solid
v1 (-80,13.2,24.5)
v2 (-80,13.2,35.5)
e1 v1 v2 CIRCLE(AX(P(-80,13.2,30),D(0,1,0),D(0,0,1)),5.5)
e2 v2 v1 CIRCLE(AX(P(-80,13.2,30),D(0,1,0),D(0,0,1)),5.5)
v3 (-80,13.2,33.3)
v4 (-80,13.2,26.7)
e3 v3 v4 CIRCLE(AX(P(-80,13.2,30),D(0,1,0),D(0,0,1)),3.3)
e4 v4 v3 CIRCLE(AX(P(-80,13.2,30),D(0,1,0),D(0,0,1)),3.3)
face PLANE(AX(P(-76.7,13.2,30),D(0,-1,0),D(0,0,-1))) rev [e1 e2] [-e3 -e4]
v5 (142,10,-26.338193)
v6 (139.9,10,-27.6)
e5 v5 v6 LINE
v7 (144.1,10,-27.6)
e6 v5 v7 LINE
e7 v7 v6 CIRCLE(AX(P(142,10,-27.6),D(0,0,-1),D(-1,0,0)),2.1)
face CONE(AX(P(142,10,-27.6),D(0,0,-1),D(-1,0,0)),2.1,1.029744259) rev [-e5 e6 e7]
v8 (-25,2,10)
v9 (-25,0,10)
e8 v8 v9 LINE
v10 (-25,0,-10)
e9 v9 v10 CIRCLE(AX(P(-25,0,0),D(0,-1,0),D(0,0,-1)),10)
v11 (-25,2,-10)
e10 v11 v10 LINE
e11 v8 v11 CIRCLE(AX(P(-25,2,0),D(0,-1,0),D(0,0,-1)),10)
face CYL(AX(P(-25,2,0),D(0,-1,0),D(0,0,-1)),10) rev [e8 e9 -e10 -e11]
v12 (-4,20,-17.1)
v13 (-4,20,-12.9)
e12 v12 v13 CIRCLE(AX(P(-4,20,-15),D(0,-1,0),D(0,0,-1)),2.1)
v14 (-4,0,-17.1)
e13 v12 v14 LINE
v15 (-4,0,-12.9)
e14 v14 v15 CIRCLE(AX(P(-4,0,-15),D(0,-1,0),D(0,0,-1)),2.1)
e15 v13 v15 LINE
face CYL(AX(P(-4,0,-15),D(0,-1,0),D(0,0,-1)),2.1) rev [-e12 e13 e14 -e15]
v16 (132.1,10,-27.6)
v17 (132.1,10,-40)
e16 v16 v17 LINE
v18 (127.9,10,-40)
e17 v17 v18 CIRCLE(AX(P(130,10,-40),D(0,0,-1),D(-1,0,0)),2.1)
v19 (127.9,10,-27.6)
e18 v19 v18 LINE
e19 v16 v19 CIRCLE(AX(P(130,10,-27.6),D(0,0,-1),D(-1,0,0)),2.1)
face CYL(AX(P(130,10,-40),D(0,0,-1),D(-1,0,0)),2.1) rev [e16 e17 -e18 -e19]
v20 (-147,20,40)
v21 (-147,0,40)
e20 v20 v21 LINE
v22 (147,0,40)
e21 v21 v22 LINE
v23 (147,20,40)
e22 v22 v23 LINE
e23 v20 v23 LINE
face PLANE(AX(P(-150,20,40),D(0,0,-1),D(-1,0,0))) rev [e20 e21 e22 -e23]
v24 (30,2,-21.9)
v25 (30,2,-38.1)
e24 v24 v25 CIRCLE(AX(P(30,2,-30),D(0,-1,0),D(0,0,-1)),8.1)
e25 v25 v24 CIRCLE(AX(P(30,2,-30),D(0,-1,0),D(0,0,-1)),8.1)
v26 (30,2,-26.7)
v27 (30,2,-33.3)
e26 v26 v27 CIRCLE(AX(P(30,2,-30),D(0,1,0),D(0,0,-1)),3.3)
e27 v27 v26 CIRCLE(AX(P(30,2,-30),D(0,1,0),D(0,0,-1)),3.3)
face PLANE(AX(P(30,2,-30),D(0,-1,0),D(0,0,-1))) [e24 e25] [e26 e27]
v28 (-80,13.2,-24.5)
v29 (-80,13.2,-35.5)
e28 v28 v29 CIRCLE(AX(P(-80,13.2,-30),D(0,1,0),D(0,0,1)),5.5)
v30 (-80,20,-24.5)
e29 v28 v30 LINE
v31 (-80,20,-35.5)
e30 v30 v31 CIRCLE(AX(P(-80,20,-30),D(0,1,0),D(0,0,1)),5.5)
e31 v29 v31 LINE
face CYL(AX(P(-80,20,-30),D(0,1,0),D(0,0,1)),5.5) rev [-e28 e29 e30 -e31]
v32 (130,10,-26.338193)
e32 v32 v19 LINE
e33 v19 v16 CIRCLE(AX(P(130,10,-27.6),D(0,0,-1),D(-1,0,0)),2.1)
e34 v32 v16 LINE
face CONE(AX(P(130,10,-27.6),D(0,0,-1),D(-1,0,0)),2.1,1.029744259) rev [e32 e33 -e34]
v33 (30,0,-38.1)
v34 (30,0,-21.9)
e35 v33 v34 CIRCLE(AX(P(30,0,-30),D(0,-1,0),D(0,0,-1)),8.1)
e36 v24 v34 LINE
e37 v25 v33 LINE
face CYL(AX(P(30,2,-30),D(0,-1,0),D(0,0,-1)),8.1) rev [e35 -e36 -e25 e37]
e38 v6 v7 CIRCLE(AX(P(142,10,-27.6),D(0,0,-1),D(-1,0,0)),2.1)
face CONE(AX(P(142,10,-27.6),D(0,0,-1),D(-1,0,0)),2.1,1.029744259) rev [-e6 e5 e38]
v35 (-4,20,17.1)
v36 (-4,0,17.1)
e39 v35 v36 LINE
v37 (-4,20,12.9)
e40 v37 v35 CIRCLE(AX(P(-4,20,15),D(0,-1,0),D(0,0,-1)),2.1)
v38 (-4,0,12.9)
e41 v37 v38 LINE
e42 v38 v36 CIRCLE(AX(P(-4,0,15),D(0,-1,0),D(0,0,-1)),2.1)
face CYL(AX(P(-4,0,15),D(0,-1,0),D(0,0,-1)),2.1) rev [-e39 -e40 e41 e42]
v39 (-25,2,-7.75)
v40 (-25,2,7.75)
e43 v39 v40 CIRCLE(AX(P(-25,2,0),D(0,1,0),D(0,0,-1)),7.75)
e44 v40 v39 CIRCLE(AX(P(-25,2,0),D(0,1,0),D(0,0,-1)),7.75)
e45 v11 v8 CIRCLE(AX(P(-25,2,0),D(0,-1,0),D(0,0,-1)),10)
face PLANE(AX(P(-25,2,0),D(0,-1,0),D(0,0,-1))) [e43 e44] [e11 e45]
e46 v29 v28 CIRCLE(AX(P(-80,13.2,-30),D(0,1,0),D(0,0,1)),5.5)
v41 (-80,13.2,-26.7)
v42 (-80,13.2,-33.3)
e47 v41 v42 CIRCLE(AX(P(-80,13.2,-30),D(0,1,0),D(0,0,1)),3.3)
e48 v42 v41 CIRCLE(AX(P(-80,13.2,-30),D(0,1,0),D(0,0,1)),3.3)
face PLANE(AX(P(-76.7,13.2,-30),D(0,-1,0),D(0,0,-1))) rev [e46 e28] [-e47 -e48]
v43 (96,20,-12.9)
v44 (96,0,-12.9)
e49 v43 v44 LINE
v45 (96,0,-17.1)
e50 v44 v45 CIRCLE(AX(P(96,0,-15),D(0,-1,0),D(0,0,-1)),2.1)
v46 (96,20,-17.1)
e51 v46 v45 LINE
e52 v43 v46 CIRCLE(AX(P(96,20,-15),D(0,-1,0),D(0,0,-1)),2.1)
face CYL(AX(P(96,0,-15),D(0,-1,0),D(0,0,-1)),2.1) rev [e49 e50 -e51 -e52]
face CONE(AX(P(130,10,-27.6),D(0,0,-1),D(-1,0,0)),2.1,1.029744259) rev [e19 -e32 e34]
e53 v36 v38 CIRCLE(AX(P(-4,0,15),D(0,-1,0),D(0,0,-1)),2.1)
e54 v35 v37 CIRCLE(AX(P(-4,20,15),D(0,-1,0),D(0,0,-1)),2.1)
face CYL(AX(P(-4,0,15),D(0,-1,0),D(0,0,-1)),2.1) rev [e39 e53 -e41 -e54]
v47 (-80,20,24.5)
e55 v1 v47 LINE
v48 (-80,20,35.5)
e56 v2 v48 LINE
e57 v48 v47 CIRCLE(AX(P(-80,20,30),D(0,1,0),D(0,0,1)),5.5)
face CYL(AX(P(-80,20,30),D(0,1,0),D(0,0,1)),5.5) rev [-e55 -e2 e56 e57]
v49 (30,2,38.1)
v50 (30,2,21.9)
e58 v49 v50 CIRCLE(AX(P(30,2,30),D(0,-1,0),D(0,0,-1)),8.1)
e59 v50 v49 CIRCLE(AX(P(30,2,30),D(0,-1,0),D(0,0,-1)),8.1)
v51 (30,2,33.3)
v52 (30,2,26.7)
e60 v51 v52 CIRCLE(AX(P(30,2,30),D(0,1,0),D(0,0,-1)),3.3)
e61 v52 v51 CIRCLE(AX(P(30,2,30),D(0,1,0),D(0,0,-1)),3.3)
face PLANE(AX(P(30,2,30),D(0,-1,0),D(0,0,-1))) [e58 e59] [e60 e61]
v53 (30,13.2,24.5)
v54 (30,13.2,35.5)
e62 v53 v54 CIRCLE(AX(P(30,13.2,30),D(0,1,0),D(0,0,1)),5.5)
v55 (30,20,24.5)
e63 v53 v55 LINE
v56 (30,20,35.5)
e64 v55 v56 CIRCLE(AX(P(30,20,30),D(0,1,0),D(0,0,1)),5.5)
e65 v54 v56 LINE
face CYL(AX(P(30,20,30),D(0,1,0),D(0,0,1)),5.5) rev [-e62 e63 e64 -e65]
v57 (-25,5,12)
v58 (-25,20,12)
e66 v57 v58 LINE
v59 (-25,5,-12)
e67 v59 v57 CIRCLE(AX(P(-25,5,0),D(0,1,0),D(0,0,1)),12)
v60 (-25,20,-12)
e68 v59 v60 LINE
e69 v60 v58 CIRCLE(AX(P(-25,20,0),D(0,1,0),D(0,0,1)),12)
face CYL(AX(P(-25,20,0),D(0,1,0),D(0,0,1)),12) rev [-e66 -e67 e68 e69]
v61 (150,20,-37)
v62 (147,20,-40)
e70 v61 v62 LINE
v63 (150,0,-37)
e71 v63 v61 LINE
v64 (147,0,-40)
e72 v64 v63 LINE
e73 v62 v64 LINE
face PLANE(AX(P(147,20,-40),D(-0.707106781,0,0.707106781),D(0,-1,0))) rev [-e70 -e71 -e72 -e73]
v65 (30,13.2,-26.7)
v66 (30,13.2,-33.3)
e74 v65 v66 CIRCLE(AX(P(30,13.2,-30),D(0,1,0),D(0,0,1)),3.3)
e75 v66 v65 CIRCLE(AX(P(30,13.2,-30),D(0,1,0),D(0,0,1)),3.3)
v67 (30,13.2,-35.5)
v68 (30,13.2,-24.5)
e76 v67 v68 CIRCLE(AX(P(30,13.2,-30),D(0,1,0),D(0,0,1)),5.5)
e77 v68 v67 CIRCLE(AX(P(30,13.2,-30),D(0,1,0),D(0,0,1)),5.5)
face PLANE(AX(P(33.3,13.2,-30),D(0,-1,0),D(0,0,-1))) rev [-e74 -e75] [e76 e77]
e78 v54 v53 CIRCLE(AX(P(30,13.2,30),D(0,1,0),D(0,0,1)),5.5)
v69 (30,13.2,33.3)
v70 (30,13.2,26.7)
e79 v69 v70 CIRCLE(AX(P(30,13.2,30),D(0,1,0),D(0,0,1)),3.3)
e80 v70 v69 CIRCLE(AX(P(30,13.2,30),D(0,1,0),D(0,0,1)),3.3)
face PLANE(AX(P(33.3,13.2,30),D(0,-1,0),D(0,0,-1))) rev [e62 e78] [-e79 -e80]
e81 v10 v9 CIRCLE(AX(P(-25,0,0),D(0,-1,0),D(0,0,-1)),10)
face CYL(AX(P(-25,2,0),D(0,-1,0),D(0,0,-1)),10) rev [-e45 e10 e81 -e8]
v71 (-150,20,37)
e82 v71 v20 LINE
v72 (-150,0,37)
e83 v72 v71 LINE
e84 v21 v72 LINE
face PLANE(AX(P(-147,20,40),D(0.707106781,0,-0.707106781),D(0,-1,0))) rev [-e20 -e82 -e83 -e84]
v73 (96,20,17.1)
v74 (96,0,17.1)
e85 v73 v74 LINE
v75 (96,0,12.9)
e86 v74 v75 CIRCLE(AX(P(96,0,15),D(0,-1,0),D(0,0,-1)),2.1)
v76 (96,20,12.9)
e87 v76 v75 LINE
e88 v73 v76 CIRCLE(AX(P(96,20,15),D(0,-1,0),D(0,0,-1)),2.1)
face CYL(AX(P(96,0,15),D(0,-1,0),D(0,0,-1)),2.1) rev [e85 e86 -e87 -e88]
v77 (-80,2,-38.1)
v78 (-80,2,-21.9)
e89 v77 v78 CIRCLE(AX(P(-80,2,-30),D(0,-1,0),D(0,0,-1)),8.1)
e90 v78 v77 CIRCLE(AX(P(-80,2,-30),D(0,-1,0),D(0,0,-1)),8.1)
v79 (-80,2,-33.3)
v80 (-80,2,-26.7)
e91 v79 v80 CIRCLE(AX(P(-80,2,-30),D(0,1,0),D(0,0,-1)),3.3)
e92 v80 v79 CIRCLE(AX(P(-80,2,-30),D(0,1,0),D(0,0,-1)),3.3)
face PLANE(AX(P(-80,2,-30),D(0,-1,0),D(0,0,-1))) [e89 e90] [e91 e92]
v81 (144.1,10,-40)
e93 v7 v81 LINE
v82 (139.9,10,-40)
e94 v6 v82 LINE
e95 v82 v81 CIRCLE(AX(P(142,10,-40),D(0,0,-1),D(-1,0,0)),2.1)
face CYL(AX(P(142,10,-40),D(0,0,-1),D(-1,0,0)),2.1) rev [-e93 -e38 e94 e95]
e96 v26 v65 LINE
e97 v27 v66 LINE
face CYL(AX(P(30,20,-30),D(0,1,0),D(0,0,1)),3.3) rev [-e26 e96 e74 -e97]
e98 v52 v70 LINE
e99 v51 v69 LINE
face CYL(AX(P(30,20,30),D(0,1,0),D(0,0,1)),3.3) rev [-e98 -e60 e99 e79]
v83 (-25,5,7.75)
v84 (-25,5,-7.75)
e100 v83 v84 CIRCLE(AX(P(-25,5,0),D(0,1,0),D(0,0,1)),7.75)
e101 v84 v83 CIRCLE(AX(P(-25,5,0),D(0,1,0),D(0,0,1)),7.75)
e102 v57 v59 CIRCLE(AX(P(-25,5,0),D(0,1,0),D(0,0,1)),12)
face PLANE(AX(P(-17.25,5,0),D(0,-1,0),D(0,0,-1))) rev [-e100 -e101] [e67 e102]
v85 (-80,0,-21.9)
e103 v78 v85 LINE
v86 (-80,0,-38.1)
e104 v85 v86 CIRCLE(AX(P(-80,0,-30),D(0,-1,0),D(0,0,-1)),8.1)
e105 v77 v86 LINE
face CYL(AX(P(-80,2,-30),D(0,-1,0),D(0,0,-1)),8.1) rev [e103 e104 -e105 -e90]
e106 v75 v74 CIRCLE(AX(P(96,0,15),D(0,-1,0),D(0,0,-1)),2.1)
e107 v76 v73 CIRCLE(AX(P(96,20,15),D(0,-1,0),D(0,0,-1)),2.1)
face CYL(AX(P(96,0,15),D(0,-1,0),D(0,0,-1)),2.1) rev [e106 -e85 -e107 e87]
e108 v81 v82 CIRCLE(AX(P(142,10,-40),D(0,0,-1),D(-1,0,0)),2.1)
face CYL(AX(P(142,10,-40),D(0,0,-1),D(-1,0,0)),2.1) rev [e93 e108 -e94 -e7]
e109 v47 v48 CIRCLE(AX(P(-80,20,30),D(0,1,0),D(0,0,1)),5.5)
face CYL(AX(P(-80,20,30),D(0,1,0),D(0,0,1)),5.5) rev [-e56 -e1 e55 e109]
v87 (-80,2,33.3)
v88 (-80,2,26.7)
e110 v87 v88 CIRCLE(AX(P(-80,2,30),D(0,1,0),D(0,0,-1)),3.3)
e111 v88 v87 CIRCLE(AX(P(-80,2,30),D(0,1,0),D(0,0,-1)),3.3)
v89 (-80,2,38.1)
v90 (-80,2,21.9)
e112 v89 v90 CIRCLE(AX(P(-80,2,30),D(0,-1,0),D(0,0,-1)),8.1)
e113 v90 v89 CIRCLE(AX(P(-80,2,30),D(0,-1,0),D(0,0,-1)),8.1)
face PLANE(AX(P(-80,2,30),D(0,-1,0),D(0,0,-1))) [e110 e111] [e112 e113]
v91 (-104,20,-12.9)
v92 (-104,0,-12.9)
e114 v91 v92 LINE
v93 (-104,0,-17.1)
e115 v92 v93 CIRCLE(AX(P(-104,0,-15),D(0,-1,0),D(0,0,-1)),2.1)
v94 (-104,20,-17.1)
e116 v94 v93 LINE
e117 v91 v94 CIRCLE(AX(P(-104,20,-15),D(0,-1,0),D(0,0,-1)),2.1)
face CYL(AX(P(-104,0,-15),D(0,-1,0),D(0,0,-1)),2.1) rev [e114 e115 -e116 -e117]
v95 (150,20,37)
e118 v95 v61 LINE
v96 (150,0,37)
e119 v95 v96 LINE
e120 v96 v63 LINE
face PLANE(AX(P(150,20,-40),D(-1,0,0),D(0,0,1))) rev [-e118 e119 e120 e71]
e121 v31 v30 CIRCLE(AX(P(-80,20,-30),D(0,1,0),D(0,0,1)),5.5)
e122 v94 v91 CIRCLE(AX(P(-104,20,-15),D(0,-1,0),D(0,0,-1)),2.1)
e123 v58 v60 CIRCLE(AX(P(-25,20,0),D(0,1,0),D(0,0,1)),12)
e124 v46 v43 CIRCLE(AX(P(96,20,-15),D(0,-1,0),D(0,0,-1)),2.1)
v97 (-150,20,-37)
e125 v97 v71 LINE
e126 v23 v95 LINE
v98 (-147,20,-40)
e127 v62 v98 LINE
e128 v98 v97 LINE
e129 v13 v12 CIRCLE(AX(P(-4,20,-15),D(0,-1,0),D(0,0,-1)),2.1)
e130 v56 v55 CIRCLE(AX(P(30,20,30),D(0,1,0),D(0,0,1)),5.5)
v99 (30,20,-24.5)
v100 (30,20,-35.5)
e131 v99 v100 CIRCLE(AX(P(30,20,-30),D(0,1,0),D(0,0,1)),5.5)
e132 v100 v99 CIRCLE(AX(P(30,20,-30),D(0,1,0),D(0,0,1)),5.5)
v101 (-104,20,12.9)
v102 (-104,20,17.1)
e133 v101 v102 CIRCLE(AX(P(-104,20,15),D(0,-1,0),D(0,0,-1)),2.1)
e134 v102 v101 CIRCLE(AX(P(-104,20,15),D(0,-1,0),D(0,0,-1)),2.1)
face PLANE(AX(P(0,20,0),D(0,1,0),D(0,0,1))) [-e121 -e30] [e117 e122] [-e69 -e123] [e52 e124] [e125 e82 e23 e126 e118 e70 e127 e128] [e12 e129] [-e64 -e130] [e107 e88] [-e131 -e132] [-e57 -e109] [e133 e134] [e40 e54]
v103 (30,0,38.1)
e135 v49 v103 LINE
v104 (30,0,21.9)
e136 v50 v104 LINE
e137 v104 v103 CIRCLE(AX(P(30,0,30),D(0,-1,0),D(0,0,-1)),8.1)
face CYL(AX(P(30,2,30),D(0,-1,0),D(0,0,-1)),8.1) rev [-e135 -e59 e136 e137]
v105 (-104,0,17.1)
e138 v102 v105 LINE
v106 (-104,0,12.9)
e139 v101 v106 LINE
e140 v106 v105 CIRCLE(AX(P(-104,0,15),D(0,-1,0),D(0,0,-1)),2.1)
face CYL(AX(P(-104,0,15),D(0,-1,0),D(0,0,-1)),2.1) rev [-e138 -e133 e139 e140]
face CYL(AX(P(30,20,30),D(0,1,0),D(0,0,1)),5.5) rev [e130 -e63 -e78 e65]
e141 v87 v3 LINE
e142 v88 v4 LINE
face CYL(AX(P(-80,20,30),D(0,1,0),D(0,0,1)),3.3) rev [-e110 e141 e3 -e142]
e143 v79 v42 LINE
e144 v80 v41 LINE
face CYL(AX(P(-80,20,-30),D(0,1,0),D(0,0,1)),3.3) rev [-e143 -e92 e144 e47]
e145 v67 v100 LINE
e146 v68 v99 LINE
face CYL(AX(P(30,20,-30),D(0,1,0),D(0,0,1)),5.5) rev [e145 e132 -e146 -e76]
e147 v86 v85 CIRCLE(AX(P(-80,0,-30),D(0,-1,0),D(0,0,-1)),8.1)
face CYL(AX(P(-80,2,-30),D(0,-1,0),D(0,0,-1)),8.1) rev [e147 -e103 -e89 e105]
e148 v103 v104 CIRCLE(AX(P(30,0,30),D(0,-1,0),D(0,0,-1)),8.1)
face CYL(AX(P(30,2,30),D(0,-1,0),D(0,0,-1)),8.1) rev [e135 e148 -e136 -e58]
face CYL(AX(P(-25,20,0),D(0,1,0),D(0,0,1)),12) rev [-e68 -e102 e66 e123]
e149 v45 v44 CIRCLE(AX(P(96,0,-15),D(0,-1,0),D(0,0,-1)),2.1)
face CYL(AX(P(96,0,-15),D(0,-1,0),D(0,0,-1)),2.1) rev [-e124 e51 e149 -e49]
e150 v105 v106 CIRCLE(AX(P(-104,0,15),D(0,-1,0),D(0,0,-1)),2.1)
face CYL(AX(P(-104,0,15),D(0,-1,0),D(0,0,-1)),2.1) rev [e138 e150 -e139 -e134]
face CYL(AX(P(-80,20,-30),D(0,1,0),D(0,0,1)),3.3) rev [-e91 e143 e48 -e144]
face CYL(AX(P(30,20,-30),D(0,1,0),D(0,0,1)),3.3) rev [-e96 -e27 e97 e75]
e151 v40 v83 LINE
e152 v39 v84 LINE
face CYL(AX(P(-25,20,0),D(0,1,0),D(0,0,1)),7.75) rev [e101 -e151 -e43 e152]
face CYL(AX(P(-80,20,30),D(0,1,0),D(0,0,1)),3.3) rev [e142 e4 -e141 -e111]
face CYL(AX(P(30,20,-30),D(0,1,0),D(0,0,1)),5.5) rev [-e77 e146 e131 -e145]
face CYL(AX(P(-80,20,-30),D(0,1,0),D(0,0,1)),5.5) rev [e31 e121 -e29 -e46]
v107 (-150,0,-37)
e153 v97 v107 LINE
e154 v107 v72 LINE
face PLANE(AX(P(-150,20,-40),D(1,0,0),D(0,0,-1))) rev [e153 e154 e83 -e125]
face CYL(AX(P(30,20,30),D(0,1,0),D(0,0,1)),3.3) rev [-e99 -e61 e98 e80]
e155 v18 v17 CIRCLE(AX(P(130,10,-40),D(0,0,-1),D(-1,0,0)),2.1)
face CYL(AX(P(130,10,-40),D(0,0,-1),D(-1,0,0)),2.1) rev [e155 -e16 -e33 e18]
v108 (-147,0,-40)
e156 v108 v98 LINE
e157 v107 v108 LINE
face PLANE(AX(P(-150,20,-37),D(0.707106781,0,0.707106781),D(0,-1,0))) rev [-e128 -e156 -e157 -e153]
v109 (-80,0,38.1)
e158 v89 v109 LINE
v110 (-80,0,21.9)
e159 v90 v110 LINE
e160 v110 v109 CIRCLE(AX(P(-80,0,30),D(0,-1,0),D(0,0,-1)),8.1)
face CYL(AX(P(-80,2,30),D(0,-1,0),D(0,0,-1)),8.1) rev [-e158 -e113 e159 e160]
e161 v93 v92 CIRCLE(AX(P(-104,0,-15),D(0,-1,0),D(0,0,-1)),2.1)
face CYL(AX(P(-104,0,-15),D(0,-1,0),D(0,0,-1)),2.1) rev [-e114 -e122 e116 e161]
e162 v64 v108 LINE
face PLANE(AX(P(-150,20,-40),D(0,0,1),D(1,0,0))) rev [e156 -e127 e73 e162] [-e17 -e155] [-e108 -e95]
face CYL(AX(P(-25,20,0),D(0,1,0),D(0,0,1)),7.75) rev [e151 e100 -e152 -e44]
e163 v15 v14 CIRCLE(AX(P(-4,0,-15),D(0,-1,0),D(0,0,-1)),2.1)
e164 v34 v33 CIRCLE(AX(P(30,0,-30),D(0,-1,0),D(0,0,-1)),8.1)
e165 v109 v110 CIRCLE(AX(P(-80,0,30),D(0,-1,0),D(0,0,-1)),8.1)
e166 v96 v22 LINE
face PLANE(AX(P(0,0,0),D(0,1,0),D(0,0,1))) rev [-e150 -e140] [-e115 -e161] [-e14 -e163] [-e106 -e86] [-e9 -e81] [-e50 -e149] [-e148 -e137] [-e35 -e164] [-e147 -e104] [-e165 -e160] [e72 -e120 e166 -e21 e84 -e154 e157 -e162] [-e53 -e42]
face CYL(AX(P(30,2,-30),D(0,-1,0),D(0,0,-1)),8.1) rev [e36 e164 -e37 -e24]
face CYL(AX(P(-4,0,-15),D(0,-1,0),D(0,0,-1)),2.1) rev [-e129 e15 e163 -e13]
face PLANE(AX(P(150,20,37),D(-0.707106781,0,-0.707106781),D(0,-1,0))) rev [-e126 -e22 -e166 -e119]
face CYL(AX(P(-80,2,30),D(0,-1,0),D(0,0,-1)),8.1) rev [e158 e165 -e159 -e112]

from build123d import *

# Parameters (mm, degrees)
SKETCH_1_W                = 300
SKETCH_1_H                = 80
EXTRUDE_1_DEPTH           = 20
CHAMFER_1_SIZE            = 3
HOLE_WIZARD_1_D           = 15.5
HOLE_WIZARD_1_DEPTH       = 25
HOLE_WIZARD_1_CBORE_D     = 24
HOLE_WIZARD_1_CBORE_DEPTH = 15
HOLE_WIZARD_1_TIP         = 4.656669797
HOLE_WIZARD_0_D           = 6.6
HOLE_WIZARD_0_DEPTH       = 25
HOLE_WIZARD_0_CBORE_D     = 11
HOLE_WIZARD_0_CBORE_DEPTH = 6.8
HOLE_WIZARD_0_TIP         = 1.982840043
SKETCH_6_R                = 10
SKETCH_6_R_2              = 8.1
CUT_EXTRUDE_1_DEPTH       = 2
HOLE_WIZARD_M5_1_D        = 4.2
HOLE_WIZARD_M5_2_D        = 4.2
HOLE_WIZARD_M5_2_DEPTH    = 12.4
HOLE_WIZARD_M5_2_TIP      = 1.2618073


with BuildPart() as part:
    # 草图1 → 凸台-拉伸1 (new body)
    with BuildSketch(Plane(origin=(0, 0, 0), x_dir=(1, 0, 0), z_dir=(0, 1, 0))):
        Rectangle(SKETCH_1_W, SKETCH_1_H)
    extrude(amount=EXTRUDE_1_DEPTH)

    # 倒角1
    chamfer_1_edges = [part.edges().sort_by_distance(p)[0] for p in [
        (150, 10, 40),
        (-150, 10, 40),
        (-150, 10, -40),
        (150, 10, -40),
    ]]
    chamfer(chamfer_1_edges, length=CHAMFER_1_SIZE)

    # 打孔尺寸(%根据)内六角圆柱头螺钉的类型1
    with Locations(Plane(origin=(0, 20, 0), x_dir=(1, 0, 0), z_dir=(0, 1, 0))):
        with Locations((-25, 0)):
            CounterBoreHole(HOLE_WIZARD_1_D / 2, HOLE_WIZARD_1_CBORE_D / 2, HOLE_WIZARD_1_CBORE_DEPTH, depth=HOLE_WIZARD_1_DEPTH)
            with Locations((0, 0, -(HOLE_WIZARD_1_DEPTH + HOLE_WIZARD_1_TIP / 2))):  # 118° drill point
                Cone(0, HOLE_WIZARD_1_D / 2, HOLE_WIZARD_1_TIP, mode=Mode.SUBTRACT)

    # 打孔尺寸(%根据)内六角圆柱头螺钉的类型0
    with Locations(Plane(origin=(0, 20, 0), x_dir=(1, 0, 0), z_dir=(0, 1, 0))):
        with Locations((30, 30), (-80, 30), (30, -30), (-80, -30)):
            CounterBoreHole(HOLE_WIZARD_0_D / 2, HOLE_WIZARD_0_CBORE_D / 2, HOLE_WIZARD_0_CBORE_DEPTH, depth=HOLE_WIZARD_0_DEPTH)
            with Locations((0, 0, -(HOLE_WIZARD_0_DEPTH + HOLE_WIZARD_0_TIP / 2))):  # 118° drill point
                Cone(0, HOLE_WIZARD_0_D / 2, HOLE_WIZARD_0_TIP, mode=Mode.SUBTRACT)

    # 草图6 → 切除-拉伸1 (cut)
    with BuildSketch(Plane.XZ):
        with Locations(Location((-25, 0, 0), (0, 0, 270))):
            Circle(SKETCH_6_R)
        with Locations(Location((30, -30, 0), (0, 0, 270))):
            Circle(SKETCH_6_R_2)
        with Locations(Location((-80, -30, 0), (0, 0, 270))):
            Circle(SKETCH_6_R_2)
        with Locations(Location((30, 30, 0), (0, 0, 270))):
            Circle(SKETCH_6_R_2)
        with Locations(Location((-80, 30, 0), (0, 0, 270))):
            Circle(SKETCH_6_R_2)
    extrude(amount=-CUT_EXTRUDE_1_DEPTH, mode=Mode.SUBTRACT)

    # M5 螺纹孔1 (through all)
    with Locations(Plane(origin=(0, 0, 0), x_dir=(-1, 0, 0), z_dir=(0, -1, 0))):
        with Locations((-96, -15), (-96, 15), (4, -15), (4, 15), (104, -15), (104, 15)):
            Hole(HOLE_WIZARD_M5_1_D / 2)

    # M5 螺纹孔2
    with Locations(Plane(origin=(0, 0, -40), x_dir=(-1, 0, 0), z_dir=(0, 0, -1))):
        with Locations((-142, 10), (-130, 10)):
            Hole(HOLE_WIZARD_M5_2_D / 2, depth=HOLE_WIZARD_M5_2_DEPTH)
            with Locations((0, 0, -(HOLE_WIZARD_M5_2_DEPTH + HOLE_WIZARD_M5_2_TIP / 2))):  # 118° drill point
                Cone(0, HOLE_WIZARD_M5_2_D / 2, HOLE_WIZARD_M5_2_TIP, mode=Mode.SUBTRACT)


solid = part.part
